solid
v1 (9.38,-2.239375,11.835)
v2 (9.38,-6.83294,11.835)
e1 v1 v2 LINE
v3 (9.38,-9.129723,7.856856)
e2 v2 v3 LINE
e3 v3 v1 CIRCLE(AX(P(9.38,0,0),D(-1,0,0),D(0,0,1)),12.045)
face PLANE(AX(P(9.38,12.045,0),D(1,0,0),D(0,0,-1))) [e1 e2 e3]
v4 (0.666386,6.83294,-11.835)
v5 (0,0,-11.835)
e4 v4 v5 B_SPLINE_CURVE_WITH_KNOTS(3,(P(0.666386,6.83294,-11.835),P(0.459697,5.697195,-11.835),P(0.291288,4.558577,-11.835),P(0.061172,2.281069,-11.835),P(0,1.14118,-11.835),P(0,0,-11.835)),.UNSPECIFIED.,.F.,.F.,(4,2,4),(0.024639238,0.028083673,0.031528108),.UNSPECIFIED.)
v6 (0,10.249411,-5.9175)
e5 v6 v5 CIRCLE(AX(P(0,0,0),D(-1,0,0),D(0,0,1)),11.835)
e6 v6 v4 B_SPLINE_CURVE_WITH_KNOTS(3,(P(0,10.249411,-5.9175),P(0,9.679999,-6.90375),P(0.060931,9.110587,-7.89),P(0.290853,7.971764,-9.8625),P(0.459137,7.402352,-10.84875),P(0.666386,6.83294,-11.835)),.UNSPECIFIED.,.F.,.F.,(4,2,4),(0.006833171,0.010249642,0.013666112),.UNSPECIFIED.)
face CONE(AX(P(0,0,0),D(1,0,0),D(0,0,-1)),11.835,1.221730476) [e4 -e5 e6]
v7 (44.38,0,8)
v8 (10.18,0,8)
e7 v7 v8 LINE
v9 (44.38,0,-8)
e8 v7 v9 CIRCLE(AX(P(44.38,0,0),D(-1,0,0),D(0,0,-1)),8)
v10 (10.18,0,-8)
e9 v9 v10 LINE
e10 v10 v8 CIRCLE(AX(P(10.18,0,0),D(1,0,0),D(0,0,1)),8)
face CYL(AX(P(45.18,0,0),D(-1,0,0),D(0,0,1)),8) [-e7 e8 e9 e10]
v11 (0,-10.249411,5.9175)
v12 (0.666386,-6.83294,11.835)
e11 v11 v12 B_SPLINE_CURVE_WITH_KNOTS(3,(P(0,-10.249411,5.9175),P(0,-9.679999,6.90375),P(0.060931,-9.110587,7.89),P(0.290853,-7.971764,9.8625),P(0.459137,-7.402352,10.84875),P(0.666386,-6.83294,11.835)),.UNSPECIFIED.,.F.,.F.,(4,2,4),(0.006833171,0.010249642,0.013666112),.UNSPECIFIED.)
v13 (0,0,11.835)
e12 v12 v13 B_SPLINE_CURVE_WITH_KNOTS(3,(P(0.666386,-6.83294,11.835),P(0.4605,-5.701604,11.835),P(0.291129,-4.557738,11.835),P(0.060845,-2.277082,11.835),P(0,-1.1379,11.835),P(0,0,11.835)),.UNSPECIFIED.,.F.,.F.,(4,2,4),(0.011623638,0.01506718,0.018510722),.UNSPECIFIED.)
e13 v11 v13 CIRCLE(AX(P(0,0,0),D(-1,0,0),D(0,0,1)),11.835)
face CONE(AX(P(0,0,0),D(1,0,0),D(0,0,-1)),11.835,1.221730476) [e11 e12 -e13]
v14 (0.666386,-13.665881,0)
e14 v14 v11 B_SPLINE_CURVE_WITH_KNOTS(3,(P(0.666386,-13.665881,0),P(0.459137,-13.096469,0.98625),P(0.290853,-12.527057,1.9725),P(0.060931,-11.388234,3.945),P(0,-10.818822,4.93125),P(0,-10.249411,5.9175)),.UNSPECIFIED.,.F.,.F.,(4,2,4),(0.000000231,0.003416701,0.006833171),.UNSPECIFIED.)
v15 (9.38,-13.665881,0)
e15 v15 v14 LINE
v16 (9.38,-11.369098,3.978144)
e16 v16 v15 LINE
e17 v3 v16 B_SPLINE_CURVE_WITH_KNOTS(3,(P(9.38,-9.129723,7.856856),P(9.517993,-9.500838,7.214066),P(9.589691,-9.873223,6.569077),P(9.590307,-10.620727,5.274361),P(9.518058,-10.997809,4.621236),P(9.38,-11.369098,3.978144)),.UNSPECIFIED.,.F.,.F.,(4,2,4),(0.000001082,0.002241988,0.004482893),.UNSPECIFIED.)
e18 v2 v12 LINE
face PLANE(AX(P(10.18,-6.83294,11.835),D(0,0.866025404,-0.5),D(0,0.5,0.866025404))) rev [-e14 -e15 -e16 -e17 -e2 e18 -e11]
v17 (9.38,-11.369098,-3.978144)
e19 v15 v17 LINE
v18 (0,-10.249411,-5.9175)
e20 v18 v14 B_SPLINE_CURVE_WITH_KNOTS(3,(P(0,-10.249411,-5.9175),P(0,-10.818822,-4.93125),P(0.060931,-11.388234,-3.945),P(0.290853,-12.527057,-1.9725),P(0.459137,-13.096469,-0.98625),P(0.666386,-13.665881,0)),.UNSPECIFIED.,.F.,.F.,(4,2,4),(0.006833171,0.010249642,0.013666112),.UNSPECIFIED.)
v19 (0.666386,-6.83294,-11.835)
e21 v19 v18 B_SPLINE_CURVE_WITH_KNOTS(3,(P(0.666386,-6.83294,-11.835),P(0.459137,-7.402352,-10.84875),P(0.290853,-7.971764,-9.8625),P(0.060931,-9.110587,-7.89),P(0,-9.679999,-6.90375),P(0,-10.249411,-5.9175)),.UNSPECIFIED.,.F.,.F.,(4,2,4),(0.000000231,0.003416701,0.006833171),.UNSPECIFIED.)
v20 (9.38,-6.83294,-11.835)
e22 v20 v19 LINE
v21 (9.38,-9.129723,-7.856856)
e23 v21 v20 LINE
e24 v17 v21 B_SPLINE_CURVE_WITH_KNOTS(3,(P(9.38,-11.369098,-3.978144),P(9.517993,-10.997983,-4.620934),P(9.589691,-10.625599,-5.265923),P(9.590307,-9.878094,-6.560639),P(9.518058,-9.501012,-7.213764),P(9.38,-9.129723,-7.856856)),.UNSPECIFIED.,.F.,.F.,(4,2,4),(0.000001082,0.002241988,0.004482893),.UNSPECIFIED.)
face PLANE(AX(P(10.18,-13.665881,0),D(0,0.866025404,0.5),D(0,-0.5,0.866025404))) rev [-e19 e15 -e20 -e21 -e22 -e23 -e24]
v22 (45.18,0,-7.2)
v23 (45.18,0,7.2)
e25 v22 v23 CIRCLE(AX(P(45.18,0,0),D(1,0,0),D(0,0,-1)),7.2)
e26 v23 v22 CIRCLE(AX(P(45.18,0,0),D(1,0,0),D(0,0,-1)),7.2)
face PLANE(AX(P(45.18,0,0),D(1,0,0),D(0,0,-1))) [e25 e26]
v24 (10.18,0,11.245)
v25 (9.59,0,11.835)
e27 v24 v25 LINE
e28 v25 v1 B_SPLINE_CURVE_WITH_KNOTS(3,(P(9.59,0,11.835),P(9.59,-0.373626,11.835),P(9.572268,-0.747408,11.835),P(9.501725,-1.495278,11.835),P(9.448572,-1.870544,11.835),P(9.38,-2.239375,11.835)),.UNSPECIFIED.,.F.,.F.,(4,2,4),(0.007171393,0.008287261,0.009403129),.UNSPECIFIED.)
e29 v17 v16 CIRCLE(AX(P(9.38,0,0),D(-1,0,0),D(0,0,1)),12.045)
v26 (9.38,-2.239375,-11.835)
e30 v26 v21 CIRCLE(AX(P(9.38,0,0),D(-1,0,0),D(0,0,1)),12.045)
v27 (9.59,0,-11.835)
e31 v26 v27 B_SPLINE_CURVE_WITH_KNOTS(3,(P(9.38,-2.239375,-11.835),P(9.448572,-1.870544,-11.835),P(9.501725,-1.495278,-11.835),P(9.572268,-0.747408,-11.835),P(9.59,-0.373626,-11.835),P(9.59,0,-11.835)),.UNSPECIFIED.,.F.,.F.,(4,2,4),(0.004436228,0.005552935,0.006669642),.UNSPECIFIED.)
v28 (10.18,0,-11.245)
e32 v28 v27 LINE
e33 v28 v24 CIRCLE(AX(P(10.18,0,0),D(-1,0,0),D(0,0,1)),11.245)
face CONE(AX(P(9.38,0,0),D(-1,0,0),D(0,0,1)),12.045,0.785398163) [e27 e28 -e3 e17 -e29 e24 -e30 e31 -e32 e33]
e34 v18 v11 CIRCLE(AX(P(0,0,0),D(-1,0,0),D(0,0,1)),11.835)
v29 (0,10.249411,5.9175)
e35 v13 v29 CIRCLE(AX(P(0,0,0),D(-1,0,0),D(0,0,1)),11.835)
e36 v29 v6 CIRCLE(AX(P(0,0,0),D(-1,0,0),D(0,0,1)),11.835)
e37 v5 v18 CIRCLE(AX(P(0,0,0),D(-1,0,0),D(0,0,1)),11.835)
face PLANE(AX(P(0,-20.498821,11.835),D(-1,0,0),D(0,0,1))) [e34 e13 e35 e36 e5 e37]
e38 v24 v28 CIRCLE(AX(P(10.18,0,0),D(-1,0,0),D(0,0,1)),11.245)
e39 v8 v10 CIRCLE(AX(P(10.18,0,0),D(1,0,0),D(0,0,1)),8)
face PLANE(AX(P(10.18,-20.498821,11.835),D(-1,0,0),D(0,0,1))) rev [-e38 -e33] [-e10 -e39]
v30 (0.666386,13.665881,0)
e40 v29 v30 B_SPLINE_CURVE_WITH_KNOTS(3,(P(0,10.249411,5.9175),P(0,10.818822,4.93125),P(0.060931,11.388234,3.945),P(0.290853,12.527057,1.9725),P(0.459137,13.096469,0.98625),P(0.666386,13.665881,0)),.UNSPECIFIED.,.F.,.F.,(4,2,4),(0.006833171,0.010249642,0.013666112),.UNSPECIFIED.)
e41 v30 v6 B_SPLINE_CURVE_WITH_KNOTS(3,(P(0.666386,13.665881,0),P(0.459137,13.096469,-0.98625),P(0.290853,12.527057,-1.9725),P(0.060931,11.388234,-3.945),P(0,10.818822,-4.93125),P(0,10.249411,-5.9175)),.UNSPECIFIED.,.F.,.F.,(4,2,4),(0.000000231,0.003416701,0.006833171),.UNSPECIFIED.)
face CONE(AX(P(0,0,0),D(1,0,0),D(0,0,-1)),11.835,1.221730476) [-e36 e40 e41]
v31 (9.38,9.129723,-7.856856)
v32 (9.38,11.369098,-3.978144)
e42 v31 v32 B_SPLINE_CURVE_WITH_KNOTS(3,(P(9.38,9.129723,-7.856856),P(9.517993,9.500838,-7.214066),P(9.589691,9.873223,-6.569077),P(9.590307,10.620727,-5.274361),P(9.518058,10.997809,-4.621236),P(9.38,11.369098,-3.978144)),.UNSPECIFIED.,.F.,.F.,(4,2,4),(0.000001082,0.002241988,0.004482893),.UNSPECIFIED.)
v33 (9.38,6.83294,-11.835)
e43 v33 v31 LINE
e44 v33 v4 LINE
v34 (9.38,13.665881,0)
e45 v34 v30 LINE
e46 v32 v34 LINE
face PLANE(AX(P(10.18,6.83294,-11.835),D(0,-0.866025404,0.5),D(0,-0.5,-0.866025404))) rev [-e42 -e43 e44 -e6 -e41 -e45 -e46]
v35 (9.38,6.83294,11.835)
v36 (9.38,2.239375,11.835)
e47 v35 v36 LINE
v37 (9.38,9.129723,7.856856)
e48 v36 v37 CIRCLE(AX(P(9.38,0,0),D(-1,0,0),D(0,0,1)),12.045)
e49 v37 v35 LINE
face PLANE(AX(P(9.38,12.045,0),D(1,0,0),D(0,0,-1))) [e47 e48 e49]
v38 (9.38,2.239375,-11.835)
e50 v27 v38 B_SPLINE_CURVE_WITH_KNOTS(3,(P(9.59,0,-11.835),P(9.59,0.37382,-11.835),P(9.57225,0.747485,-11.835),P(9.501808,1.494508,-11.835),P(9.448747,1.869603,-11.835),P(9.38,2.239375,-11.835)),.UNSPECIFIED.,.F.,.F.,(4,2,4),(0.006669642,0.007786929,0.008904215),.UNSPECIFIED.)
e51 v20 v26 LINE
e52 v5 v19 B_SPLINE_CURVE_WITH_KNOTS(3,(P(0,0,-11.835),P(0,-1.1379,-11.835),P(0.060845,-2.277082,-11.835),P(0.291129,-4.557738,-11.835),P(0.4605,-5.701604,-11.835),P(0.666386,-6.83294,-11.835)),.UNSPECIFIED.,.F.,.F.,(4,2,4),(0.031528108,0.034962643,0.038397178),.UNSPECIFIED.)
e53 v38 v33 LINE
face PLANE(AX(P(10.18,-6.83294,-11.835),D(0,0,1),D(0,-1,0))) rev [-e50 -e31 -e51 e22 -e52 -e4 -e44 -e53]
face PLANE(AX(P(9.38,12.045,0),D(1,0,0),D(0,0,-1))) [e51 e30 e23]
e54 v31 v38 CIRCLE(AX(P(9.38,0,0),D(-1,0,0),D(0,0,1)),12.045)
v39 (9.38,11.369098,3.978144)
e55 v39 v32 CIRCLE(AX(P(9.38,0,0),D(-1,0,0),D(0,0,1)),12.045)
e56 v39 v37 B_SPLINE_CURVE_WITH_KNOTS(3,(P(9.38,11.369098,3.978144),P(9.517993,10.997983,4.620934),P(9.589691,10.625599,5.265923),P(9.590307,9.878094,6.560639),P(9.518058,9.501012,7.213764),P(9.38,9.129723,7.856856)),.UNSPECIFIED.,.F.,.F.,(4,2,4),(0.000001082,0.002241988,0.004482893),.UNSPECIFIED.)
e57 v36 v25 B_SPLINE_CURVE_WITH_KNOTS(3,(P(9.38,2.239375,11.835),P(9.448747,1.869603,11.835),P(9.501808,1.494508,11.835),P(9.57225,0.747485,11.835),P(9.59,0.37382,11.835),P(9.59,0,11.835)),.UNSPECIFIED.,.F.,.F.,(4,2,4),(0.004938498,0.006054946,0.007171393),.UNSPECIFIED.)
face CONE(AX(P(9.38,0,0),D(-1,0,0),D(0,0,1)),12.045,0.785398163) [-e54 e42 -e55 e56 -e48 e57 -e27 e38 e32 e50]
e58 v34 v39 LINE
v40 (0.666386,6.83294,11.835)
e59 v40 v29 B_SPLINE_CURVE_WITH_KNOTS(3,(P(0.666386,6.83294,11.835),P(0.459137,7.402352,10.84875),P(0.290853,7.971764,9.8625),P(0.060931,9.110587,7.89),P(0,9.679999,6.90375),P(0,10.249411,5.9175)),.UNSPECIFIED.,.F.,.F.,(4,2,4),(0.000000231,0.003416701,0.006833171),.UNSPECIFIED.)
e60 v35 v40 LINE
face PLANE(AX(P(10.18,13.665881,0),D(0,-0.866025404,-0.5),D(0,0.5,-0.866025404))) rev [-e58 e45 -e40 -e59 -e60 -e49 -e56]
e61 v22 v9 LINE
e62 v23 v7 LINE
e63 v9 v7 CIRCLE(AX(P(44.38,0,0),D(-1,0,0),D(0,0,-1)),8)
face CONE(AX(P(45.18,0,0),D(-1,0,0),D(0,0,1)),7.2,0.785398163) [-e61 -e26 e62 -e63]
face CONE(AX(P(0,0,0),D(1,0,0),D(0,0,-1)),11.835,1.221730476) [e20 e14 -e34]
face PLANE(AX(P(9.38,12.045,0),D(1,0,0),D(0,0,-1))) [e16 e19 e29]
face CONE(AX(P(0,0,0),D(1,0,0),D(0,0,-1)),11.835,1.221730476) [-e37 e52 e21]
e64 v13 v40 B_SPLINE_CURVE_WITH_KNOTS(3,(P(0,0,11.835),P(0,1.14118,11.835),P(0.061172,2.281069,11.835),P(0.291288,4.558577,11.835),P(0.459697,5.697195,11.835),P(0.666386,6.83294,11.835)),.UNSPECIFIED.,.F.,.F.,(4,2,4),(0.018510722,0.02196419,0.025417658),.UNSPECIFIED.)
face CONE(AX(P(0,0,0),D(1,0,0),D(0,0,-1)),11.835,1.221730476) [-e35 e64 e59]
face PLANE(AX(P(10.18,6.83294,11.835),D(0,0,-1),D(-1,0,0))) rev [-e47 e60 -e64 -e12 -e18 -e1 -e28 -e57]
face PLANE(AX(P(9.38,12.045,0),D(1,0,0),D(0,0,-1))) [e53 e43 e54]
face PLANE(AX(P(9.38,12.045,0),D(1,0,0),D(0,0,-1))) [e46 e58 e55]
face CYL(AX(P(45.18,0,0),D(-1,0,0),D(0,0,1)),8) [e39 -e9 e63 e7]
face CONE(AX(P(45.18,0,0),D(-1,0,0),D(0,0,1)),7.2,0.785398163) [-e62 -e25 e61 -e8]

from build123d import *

# Parameters (mm, degrees)
BASEHEAD_DEPTH = 10.18
SKETCH5_R      = 8
BASEBODY_DEPTH = 35
CHAMFER1_SIZE  = 0.8


with BuildPart() as part:
    # Sketch2 → BaseHead (new body)
    with BuildSketch(Plane(origin=(0, 0, 0), x_dir=(0, 0, -1), z_dir=(1, 0, 0))):
        Polygon((11.835, -6.832940436), (11.835, 6.832940436), (0, 13.665880872), (-11.835, 6.832940436), (-11.835, -6.832940436), (0, -13.665880872), align=None)
    extrude(amount=BASEHEAD_DEPTH)

    # Sketch3 → BearingFace (revolve, cut)
    with BuildSketch(Plane.XY, mode=Mode.PRIVATE) as bearingface_sk:
        Polygon((10.18, 13.665880872), (10.18, 11.245), (9.38, 12.045), (9.38, 13.665880872), align=None)
    revolve(bearingface_sk.sketch.rotate(Axis((-0.957090588, 0, 0), (1, 0, 0)), 90), axis=Axis((-0.957090588, 0, 0), (1, 0, 0)), mode=Mode.SUBTRACT)

    # Sketch4 → HeadChamfer (revolve, cut)
    with BuildSketch(Plane.XY):
        Polygon((0, 13.665880872), (0.66638614, 13.665880872), (0, 11.835), align=None)
    revolve(axis=Axis((-0.493528746, 0, 0), (1, 0, 0)), mode=Mode.SUBTRACT)

    # Sketch5 → BaseBody (add)
    with BuildSketch(Plane(origin=(10.18, 0, 0), x_dir=(0, 0, -1), z_dir=(1, 0, 0))):
        with Locations(Location((0, 0, 0), (0, 0, 180))):
            Circle(SKETCH5_R)
    extrude(amount=BASEBODY_DEPTH)

    # Chamfer1
    chamfer1_edges = [part.edges().sort_by_distance(p)[0] for p in [
        (45.18, 0, -8),
    ]]
    chamfer(chamfer1_edges, length=CHAMFER1_SIZE)


solid = part.part
